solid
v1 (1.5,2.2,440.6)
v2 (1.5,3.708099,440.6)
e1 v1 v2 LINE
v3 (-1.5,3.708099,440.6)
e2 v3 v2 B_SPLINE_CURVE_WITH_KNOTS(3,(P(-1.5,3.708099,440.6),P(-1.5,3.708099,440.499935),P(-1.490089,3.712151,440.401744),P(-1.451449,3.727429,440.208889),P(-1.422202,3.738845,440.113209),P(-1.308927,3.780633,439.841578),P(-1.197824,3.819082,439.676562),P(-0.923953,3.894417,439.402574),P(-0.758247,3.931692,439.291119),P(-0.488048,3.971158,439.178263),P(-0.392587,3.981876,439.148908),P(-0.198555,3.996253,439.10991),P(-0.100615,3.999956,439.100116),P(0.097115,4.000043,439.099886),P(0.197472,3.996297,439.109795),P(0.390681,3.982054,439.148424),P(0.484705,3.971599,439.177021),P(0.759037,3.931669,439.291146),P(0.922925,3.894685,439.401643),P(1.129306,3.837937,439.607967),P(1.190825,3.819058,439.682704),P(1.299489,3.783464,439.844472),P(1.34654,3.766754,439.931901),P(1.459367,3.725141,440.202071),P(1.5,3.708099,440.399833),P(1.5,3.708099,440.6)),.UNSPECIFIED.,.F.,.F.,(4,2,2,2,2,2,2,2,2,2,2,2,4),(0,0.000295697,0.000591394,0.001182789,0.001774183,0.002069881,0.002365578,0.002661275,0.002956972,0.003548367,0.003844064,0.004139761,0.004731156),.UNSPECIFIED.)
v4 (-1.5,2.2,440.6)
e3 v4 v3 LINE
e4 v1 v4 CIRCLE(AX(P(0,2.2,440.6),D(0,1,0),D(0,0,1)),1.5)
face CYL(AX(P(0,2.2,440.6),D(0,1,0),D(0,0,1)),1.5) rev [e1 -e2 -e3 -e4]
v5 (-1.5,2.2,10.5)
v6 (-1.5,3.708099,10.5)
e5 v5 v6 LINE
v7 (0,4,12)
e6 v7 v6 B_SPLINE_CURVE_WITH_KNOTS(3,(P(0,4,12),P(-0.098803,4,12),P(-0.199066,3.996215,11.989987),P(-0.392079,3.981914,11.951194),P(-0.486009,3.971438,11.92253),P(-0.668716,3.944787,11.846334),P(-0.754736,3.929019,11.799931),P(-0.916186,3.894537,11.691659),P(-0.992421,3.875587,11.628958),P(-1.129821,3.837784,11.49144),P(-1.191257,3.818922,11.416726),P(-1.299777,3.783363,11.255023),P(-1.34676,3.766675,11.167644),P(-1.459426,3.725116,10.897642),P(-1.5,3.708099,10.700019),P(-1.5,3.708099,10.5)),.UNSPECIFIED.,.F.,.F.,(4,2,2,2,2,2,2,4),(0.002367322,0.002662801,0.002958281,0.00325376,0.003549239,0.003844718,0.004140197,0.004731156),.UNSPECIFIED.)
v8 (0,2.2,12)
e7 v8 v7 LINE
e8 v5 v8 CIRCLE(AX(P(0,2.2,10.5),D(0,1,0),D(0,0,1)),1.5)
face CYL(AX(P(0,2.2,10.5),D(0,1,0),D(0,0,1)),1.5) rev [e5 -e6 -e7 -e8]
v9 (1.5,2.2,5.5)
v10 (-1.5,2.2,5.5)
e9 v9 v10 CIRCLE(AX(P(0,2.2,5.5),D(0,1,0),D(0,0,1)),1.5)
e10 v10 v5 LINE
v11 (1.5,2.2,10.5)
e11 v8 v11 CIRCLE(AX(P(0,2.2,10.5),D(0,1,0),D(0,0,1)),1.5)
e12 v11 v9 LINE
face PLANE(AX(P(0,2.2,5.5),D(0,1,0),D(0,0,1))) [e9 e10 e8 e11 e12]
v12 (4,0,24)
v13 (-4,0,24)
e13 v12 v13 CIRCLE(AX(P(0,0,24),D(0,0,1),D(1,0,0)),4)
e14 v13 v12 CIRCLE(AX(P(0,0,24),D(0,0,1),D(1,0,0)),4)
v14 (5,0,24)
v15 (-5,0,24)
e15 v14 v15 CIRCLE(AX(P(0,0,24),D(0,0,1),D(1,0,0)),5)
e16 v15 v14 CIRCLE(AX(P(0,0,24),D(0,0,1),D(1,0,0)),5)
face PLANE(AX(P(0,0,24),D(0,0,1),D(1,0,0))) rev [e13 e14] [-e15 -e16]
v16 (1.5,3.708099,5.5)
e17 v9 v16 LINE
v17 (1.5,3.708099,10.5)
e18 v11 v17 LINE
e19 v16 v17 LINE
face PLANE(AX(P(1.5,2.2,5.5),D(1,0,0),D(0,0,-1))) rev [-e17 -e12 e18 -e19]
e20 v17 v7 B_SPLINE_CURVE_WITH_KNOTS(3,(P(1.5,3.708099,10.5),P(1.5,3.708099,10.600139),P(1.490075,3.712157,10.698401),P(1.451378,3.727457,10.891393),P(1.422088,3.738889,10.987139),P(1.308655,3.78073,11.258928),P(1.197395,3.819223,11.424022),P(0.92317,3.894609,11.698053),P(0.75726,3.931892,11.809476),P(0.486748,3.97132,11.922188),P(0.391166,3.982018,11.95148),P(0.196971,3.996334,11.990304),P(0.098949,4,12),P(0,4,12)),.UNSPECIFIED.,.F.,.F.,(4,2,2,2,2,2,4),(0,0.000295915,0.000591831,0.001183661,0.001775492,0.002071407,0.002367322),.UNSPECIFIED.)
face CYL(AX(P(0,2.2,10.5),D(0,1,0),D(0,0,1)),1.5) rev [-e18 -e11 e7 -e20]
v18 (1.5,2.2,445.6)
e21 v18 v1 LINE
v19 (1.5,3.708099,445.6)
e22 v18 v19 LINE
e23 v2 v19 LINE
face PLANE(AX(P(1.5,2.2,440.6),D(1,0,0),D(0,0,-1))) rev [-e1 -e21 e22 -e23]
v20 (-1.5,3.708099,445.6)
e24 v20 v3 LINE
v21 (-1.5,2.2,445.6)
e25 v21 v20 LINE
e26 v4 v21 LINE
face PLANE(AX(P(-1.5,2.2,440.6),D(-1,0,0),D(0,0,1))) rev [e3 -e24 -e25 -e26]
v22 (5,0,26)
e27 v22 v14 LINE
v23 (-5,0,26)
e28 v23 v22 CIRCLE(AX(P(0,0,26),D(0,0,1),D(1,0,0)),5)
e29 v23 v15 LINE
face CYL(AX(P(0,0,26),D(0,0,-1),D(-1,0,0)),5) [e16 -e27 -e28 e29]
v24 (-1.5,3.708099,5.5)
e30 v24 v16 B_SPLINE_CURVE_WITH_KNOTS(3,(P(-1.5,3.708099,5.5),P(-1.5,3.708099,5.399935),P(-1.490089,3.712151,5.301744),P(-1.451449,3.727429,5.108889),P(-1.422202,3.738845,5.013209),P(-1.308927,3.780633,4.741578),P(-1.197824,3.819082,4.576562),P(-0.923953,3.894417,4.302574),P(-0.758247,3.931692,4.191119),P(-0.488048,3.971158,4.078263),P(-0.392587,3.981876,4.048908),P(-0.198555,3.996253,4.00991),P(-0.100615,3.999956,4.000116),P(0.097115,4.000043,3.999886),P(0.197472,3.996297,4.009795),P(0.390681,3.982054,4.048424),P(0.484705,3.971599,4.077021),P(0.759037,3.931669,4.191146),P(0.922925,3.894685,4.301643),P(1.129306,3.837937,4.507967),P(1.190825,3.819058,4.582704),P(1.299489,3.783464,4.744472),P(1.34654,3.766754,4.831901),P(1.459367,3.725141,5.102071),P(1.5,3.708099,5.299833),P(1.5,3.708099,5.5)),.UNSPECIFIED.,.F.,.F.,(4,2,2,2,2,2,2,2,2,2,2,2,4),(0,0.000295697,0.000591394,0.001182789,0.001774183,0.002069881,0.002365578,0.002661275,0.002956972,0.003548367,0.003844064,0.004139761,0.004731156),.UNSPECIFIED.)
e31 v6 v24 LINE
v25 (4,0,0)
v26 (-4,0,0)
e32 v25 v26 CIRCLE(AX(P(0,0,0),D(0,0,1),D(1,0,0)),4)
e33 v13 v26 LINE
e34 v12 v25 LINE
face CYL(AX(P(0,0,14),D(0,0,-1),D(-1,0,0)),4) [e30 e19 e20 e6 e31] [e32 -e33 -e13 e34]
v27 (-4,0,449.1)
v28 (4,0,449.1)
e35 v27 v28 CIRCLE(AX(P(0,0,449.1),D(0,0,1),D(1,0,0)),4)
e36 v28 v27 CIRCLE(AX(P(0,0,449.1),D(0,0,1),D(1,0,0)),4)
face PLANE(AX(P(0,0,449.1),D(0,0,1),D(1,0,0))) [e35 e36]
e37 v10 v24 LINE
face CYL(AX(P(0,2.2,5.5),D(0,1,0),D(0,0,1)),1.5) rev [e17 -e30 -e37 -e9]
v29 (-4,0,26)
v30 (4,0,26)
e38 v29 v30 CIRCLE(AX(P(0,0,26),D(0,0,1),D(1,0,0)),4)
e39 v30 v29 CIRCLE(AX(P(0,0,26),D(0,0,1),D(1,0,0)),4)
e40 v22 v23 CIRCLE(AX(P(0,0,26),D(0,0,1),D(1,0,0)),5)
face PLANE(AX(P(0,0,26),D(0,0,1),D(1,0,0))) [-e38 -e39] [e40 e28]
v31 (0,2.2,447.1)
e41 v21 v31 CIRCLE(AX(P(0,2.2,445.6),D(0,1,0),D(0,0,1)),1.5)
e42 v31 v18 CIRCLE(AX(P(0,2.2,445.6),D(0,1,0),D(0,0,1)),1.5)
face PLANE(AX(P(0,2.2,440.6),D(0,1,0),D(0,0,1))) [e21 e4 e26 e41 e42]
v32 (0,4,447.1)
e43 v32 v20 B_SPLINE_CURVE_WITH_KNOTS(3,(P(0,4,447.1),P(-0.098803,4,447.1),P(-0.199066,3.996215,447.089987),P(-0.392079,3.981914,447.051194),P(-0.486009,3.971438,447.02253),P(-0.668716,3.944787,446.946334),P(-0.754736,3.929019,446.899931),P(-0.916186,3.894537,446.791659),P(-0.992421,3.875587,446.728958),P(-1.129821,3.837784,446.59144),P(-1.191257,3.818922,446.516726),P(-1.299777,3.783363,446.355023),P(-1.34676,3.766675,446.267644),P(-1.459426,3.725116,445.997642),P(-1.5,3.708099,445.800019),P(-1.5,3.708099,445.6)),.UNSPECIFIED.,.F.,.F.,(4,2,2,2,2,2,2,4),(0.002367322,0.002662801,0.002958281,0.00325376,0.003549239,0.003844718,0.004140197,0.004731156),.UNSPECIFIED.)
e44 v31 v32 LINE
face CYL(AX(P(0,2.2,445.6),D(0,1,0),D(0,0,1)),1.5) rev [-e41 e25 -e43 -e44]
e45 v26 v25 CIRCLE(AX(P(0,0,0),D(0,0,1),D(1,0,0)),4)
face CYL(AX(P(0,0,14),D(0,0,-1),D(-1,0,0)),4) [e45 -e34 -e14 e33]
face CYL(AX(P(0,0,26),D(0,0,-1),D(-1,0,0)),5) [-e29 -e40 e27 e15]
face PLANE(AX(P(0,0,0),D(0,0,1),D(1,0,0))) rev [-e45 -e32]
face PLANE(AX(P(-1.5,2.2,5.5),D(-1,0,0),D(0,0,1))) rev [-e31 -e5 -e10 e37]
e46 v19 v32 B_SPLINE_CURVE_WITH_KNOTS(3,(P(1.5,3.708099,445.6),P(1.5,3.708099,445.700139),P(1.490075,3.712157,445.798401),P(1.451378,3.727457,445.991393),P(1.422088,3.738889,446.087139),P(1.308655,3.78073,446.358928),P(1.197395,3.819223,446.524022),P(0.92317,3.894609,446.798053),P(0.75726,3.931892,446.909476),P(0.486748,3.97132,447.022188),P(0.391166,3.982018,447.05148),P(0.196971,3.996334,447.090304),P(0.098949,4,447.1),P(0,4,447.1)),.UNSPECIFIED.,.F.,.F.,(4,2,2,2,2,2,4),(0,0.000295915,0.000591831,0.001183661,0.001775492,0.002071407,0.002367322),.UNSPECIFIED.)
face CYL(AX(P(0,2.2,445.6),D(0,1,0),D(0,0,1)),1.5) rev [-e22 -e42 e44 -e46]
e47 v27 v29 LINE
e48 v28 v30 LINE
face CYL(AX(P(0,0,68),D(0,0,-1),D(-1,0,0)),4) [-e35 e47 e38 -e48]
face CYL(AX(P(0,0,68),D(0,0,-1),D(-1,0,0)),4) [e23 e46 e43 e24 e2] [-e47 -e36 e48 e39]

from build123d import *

# Parameters (mm, degrees)
SKETCH3_R           = 4
BOSS_EXTRUDE2_DEPTH = 14
SKETCH4_R           = 4
BOSS_EXTRUDE3_DEPTH = 10
SKETCH5_R           = 5
BOSS_EXTRUDE4_DEPTH = 2
CUT_EXTRUDE1_DEPTH  = 1.8
SKETCH7_R           = 4
BOSS_EXTRUDE5_DEPTH = 42
SKETCH8_R           = 4
BOSS_EXTRUDE7_DEPTH = 150
SKETCH9_R           = 4
BOSS_EXTRUDE8_DEPTH = 198
SKETCH10_R          = 4
BOSS_EXTRUDE9_DEPTH = 33.1
CUT_EXTRUDE2_DEPTH  = 1.8


with BuildPart() as part:
    # Sketch3 → Boss-Extrude2 (new body)
    with BuildSketch(Plane.XY):
        Circle(SKETCH3_R)
    extrude(amount=BOSS_EXTRUDE2_DEPTH)

    # Sketch4 → Boss-Extrude3 (add)
    with BuildSketch(Plane.XY.offset(14)):
        Circle(SKETCH4_R)
    extrude(amount=BOSS_EXTRUDE3_DEPTH)

    # Sketch5 → Boss-Extrude4 (add)
    with BuildSketch(Plane.XY.offset(24)):
        Circle(SKETCH5_R)
    extrude(amount=BOSS_EXTRUDE4_DEPTH)

    # Sketch6 → Cut-Extrude1 (cut)
    with BuildSketch(Plane(origin=(0, 4, 0), x_dir=(1, 0, 0), z_dir=(0, 1, 0))):
        with BuildLine():
            Line((1.5, -5.5), (1.5, -10.5))
            ThreePointArc((1.5, -10.5), (0, -12), (-1.5, -10.5))
            Line((-1.5, -10.5), (-1.5, -5.5))
            ThreePointArc((-1.5, -5.5), (0, -4), (1.5, -5.5))
        make_face()
    extrude(amount=-CUT_EXTRUDE1_DEPTH, mode=Mode.SUBTRACT)

    # Sketch7 → Boss-Extrude5 (add)
    with BuildSketch(Plane.XY.offset(26)):
        Circle(SKETCH7_R)
    extrude(amount=BOSS_EXTRUDE5_DEPTH)

    # Sketch8 → Boss-Extrude7 (add)
    with BuildSketch(Plane.XY.offset(68)):
        Circle(SKETCH8_R)
    extrude(amount=BOSS_EXTRUDE7_DEPTH)

    # Sketch9 → Boss-Extrude8 (add)
    with BuildSketch(Plane.XY.offset(218)):
        Circle(SKETCH9_R)
    extrude(amount=BOSS_EXTRUDE8_DEPTH)

    # Sketch10 → Boss-Extrude9 (add)
    with BuildSketch(Plane.XY.offset(416)):
        Circle(SKETCH10_R)
    extrude(amount=BOSS_EXTRUDE9_DEPTH)

    # Sketch13 → Cut-Extrude2 (cut)
    with BuildSketch(Plane(origin=(0, 4, 0), x_dir=(1, 0, 0), z_dir=(0, 1, 0))):
        with BuildLine():
            Line((1.5, -440.6), (1.5, -445.6))
            ThreePointArc((1.5, -445.6), (0, -447.1), (-1.5, -445.6))
            Line((-1.5, -445.6), (-1.5, -440.6))
            ThreePointArc((-1.5, -440.6), (0, -439.1), (1.5, -440.6))
        make_face()
    extrude(amount=-CUT_EXTRUDE2_DEPTH, mode=Mode.SUBTRACT)


solid = part.part
